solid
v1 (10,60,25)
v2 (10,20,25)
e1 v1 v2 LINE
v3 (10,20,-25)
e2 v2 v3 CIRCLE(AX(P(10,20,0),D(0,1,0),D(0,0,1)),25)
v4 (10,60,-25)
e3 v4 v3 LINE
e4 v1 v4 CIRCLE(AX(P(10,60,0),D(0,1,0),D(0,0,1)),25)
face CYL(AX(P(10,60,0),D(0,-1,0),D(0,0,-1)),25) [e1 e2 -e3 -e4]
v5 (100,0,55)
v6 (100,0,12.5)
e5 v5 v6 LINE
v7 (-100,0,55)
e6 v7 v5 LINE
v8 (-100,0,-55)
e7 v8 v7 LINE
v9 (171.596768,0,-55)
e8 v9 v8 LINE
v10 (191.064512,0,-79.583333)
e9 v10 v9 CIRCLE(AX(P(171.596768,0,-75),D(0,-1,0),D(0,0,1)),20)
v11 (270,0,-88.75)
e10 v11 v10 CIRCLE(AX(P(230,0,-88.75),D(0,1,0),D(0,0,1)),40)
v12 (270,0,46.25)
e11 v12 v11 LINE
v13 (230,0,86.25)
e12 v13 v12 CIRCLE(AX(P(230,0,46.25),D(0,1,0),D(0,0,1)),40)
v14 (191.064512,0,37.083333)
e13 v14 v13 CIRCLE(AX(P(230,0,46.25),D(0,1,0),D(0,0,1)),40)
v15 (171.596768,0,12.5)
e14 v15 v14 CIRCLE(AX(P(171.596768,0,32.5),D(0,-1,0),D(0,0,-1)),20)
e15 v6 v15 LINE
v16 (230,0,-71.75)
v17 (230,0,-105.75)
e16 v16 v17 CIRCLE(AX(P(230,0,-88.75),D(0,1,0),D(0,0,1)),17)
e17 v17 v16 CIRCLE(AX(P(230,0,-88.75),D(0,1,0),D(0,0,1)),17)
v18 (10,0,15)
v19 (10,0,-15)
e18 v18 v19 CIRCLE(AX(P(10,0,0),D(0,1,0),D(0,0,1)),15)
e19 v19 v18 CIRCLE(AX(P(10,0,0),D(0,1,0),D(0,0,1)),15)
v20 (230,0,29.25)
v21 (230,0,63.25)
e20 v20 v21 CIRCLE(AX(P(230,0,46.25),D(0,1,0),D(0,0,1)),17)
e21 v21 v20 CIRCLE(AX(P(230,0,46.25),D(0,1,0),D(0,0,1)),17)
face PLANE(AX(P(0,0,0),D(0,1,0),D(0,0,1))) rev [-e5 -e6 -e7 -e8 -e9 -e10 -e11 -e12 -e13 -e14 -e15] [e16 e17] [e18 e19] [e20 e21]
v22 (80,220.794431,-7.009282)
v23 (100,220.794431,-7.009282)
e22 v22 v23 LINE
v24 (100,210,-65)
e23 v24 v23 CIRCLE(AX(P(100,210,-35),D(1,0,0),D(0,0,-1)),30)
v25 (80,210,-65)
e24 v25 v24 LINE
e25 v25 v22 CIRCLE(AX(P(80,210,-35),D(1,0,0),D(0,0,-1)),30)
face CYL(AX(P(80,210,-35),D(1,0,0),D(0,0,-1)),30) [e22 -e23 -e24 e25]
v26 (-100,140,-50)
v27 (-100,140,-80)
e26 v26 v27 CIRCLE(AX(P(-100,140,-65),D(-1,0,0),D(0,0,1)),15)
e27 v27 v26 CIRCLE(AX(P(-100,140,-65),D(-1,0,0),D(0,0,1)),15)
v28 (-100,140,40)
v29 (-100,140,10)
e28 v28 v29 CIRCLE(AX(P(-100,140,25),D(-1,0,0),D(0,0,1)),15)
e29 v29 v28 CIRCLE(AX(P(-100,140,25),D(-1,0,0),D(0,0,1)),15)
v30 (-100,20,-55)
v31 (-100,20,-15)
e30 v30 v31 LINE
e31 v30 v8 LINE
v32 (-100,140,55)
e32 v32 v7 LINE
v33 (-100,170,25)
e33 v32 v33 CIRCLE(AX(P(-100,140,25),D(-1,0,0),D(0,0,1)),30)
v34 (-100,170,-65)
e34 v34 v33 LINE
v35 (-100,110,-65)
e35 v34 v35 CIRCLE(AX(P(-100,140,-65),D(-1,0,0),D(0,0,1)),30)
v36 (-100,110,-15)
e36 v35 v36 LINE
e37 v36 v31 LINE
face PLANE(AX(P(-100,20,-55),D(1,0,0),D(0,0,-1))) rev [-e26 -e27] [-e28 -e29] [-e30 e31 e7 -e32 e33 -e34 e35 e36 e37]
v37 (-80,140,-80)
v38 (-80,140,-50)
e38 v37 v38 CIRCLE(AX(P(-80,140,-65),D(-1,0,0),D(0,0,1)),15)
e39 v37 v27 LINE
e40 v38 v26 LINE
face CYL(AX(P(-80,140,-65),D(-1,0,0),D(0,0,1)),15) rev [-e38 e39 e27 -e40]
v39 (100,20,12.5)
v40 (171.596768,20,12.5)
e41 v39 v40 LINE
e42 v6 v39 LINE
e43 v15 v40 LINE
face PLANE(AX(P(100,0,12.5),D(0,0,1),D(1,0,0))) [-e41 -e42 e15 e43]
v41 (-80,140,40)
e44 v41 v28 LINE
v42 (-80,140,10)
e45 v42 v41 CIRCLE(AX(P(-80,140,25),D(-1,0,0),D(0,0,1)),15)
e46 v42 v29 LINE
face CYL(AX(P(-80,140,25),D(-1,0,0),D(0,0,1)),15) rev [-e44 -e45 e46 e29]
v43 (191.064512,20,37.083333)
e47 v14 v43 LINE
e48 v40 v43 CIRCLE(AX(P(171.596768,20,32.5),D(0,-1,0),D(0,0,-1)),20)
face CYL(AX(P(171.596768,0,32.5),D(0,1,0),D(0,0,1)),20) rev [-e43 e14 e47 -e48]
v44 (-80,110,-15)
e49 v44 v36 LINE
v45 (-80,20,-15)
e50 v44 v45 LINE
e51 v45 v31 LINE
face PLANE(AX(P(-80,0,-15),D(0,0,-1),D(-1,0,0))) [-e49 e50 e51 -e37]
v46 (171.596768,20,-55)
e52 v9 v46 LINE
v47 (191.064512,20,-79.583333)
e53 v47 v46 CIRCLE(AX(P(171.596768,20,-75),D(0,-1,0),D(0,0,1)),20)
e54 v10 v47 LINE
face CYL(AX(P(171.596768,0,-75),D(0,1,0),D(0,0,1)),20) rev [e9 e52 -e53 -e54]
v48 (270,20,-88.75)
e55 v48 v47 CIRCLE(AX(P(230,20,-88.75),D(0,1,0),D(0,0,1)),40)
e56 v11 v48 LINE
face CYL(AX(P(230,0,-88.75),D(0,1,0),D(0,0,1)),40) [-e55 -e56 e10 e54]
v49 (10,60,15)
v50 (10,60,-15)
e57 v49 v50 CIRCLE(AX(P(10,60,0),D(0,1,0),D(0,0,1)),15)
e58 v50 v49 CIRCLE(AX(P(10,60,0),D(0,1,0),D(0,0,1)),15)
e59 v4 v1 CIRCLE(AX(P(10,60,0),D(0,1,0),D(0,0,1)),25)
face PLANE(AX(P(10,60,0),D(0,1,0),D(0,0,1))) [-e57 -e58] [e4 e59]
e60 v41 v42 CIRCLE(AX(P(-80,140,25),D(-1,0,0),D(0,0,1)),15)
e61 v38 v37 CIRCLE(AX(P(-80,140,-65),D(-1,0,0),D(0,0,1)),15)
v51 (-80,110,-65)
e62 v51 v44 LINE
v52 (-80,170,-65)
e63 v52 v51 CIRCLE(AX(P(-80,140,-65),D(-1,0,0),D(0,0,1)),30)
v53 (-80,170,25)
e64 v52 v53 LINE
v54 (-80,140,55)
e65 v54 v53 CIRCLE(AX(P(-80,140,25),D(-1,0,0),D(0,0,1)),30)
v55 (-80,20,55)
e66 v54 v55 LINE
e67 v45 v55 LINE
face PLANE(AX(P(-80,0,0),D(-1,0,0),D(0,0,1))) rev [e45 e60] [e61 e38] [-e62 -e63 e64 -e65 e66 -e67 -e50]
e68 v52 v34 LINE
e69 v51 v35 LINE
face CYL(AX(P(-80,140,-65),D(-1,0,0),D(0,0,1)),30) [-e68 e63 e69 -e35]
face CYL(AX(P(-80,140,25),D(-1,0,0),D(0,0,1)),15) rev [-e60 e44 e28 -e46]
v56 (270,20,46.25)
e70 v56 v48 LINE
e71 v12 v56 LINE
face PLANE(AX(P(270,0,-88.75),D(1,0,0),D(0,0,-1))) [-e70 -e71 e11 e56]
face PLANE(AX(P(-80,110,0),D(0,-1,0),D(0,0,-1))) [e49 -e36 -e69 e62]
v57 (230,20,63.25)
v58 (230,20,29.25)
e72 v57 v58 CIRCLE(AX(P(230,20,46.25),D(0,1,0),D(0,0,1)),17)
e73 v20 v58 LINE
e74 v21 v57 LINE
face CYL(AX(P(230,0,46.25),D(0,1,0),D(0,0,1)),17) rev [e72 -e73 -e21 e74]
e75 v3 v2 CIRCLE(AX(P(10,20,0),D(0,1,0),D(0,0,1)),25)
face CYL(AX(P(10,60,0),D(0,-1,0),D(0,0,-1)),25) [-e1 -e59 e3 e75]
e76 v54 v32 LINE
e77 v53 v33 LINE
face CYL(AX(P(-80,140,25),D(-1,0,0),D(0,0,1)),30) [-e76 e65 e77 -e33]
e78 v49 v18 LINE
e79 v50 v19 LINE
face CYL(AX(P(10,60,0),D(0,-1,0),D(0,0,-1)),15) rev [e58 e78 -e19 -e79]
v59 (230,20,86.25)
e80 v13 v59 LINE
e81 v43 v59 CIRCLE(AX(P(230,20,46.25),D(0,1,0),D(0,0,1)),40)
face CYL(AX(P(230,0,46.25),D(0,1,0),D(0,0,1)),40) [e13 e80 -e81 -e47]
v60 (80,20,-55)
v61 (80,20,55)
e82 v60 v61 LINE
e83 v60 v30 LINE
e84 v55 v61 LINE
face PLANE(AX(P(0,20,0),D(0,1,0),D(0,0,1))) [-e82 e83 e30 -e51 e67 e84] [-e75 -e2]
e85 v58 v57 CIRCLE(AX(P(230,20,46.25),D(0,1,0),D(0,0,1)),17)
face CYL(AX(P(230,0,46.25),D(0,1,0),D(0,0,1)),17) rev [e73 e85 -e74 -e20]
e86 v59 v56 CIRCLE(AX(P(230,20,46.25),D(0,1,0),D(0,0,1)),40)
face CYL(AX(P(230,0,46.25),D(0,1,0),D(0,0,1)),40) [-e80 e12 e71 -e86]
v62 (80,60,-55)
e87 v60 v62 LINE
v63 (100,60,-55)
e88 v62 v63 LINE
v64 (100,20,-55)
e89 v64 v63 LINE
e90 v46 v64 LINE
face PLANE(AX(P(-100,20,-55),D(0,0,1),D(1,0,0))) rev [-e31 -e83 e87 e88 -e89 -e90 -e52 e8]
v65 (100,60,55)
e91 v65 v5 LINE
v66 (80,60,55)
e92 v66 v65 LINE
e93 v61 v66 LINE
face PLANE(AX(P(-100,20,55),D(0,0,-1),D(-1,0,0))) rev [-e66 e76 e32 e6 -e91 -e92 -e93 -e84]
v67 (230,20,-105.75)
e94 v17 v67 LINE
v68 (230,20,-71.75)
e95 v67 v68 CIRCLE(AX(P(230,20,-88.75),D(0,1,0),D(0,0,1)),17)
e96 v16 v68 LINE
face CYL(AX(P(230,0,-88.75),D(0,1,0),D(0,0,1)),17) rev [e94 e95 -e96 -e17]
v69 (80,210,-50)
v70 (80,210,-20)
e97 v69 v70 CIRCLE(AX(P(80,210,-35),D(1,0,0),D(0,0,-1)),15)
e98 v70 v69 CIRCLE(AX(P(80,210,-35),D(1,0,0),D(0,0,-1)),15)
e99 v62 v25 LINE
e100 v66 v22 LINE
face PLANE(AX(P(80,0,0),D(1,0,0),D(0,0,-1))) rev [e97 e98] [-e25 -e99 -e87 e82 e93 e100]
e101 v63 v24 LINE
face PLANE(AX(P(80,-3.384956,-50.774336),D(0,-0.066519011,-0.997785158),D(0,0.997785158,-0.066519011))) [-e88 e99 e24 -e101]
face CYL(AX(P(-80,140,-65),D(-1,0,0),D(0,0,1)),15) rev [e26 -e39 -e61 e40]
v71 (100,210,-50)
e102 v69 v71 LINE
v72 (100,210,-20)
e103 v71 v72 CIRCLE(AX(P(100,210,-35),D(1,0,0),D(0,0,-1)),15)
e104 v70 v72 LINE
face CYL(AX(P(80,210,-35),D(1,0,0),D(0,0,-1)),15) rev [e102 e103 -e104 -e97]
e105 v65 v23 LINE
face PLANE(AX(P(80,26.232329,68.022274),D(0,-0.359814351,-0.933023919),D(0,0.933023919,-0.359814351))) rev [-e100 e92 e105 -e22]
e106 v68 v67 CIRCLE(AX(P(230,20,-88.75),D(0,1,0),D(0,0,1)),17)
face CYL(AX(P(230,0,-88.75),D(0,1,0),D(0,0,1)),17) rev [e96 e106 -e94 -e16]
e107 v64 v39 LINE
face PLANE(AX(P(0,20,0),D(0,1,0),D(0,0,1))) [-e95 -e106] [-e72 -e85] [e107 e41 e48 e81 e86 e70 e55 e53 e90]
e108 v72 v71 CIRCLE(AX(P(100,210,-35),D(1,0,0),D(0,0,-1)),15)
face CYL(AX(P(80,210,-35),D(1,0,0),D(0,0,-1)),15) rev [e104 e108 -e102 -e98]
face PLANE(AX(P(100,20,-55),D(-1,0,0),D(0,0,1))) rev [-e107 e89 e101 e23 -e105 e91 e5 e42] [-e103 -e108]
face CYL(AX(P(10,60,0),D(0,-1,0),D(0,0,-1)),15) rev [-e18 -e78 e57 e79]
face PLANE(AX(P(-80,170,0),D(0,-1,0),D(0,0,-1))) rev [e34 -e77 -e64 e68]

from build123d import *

# Parameters (mm, degrees)
BASE_PLATE_SKETCH_W                 = 200
BASE_PLATE_SKETCH_H                 = 110
BASE_PLATE_DEPTH                    = 20
SIDE_BRACKET_SKETCH_R               = 17
SIDE_BRACKET_WITH_PIVOT_HOLES_DEPTH = 20
MOUNTING_FOOT_SKETCH_R              = 15
MOUNTING_FOOT_SKETCH_W              = 70
MOUNTING_FOOT_SKETCH_H              = 20
MOUNTING_FOOT_DEPTH                 = 20
TAPERED_LUG_SKETCH_R                = 15
TAPERED_PIVOT_LUG_DEPTH             = 20
BUSHING_BOSS_SKETCH_R               = 25
BUSHING_BOSS_SKETCH_R_2             = 15
BUSHING_BOSS_50_DEPTH               = 40
BUSHING_START                       = -40
BUSHING_BORE_SKETCH_R               = 15
BUSHING_BORE_30_DEPTH               = 40


with BuildPart() as part:
    # Base Plate Sketch → Base Plate (new body)
    with BuildSketch(Plane(origin=(0, 0, 0), x_dir=(1, 0, 0), z_dir=(0, 1, 0))):
        Rectangle(BASE_PLATE_SKETCH_W, BASE_PLATE_SKETCH_H)
    extrude(amount=BASE_PLATE_DEPTH)

    # Side Bracket Sketch → Side Bracket With Pivot Holes (add)
    with BuildSketch(Plane(origin=(0, 20, 0), x_dir=(1, 0, 0), z_dir=(0, 1, 0))):
        with BuildLine():
            Line((100, 55), (100, -12.5))
            Line((100, -12.5), (171.596768069, -12.5))
            ThreePointArc((171.596768069, -12.5), (187.275841171, -20.083612979), (191.064512046, -37.083333333))
            ThreePointArc((191.064512046, -37.083333333), (225.385865095, -85.982980748), (270, -46.25))
            Line((270, -46.25), (270, 88.75))
            ThreePointArc((270, 88.75), (225.385865095, 128.482980748), (191.064512046, 79.583333333))
            ThreePointArc((191.064512046, 79.583333333), (187.275841171, 62.583612979), (171.596768069, 55))
            Line((171.596768069, 55), (100, 55))
        make_face()
        with Locations(Location((230, 88.75, 0), (0, 0, 270))):
            Circle(SIDE_BRACKET_SKETCH_R, mode=Mode.SUBTRACT)
        with Locations(Location((230, -46.25, 0), (0, 0, 270))):
            Circle(SIDE_BRACKET_SKETCH_R, mode=Mode.SUBTRACT)
    extrude(amount=-SIDE_BRACKET_WITH_PIVOT_HOLES_DEPTH)

    # Mounting Foot Sketch → Mounting Foot (add)
    # profile 1 of 2: a face of its own
    with BuildSketch(Plane.ZY.offset(100)):
        with BuildLine():
            Line((25, 170), (-65, 170))
            ThreePointArc((-65, 170), (-95, 140), (-65, 110))
            Line((-65, 110), (-15, 110))
            Line((-15, 110), (-15, 20))
            Line((-15, 20), (55, 20))
            Line((55, 20), (55, 140))
            ThreePointArc((55, 140), (46.213203436, 161.213203436), (25, 170))
        make_face()
        with Locations((-65, 140)):
            Circle(MOUNTING_FOOT_SKETCH_R, mode=Mode.SUBTRACT)
        with Locations((25, 140)):
            Circle(MOUNTING_FOOT_SKETCH_R, mode=Mode.SUBTRACT)
    # profile 2 of 2: a face of its own
    with BuildSketch(Plane.ZY.offset(100)):
        with Locations((20, 10)):
            Rectangle(MOUNTING_FOOT_SKETCH_W, MOUNTING_FOOT_SKETCH_H)
    extrude(amount=-MOUNTING_FOOT_DEPTH)

    # Tapered Lug Sketch → Tapered Pivot Lug (add)
    with BuildSketch(Plane(origin=(100, 0, 0), x_dir=(0, 0, -1), z_dir=(1, 0, 0))):
        with BuildLine():
            Line((-55, 60), (-55, 20))
            Line((-55, 20), (-12.5, 20))
            Line((-12.5, 20), (55, 20))
            Line((55, 20), (55, 60))
            Line((55, 60), (64.734513274, 206.017699115))
            Line((64.734513274, 206.017699115), (65, 210))
            ThreePointArc((65, 210), (40.489921368, 239.493402031), (7.009282442, 220.794430535))
            Line((7.009282442, 220.794430535), (-55, 60))
        make_face()
        with Locations((35, 210)):
            Circle(TAPERED_LUG_SKETCH_R, mode=Mode.SUBTRACT)
    extrude(amount=-TAPERED_PIVOT_LUG_DEPTH)

    # Bushing Boss Sketch → Bushing Boss Ø50 (add)
    with BuildSketch(Plane(origin=(0, 20, 0), x_dir=(1, 0, 0), z_dir=(0, 1, 0))):
        with Locations(Location((10, 0, 0), (0, 0, 270))):
            Circle(BUSHING_BOSS_SKETCH_R)
        with Locations(Location((10, 0, 0), (0, 0, 270))):
            Circle(BUSHING_BOSS_SKETCH_R_2, mode=Mode.SUBTRACT)
    extrude(amount=BUSHING_BOSS_50_DEPTH)

    # Bushing Bore Sketch → Bushing Bore Ø30 (cut)
    with BuildSketch(Plane(origin=(0, 20, 0), x_dir=(1, 0, 0), z_dir=(0, 1, 0)).offset(BUSHING_START)):
        with Locations(Location((10, 0, 0), (0, 0, 270))):
            Circle(BUSHING_BORE_SKETCH_R)
    extrude(amount=BUSHING_BORE_30_DEPTH, mode=Mode.SUBTRACT)


solid = part.part
